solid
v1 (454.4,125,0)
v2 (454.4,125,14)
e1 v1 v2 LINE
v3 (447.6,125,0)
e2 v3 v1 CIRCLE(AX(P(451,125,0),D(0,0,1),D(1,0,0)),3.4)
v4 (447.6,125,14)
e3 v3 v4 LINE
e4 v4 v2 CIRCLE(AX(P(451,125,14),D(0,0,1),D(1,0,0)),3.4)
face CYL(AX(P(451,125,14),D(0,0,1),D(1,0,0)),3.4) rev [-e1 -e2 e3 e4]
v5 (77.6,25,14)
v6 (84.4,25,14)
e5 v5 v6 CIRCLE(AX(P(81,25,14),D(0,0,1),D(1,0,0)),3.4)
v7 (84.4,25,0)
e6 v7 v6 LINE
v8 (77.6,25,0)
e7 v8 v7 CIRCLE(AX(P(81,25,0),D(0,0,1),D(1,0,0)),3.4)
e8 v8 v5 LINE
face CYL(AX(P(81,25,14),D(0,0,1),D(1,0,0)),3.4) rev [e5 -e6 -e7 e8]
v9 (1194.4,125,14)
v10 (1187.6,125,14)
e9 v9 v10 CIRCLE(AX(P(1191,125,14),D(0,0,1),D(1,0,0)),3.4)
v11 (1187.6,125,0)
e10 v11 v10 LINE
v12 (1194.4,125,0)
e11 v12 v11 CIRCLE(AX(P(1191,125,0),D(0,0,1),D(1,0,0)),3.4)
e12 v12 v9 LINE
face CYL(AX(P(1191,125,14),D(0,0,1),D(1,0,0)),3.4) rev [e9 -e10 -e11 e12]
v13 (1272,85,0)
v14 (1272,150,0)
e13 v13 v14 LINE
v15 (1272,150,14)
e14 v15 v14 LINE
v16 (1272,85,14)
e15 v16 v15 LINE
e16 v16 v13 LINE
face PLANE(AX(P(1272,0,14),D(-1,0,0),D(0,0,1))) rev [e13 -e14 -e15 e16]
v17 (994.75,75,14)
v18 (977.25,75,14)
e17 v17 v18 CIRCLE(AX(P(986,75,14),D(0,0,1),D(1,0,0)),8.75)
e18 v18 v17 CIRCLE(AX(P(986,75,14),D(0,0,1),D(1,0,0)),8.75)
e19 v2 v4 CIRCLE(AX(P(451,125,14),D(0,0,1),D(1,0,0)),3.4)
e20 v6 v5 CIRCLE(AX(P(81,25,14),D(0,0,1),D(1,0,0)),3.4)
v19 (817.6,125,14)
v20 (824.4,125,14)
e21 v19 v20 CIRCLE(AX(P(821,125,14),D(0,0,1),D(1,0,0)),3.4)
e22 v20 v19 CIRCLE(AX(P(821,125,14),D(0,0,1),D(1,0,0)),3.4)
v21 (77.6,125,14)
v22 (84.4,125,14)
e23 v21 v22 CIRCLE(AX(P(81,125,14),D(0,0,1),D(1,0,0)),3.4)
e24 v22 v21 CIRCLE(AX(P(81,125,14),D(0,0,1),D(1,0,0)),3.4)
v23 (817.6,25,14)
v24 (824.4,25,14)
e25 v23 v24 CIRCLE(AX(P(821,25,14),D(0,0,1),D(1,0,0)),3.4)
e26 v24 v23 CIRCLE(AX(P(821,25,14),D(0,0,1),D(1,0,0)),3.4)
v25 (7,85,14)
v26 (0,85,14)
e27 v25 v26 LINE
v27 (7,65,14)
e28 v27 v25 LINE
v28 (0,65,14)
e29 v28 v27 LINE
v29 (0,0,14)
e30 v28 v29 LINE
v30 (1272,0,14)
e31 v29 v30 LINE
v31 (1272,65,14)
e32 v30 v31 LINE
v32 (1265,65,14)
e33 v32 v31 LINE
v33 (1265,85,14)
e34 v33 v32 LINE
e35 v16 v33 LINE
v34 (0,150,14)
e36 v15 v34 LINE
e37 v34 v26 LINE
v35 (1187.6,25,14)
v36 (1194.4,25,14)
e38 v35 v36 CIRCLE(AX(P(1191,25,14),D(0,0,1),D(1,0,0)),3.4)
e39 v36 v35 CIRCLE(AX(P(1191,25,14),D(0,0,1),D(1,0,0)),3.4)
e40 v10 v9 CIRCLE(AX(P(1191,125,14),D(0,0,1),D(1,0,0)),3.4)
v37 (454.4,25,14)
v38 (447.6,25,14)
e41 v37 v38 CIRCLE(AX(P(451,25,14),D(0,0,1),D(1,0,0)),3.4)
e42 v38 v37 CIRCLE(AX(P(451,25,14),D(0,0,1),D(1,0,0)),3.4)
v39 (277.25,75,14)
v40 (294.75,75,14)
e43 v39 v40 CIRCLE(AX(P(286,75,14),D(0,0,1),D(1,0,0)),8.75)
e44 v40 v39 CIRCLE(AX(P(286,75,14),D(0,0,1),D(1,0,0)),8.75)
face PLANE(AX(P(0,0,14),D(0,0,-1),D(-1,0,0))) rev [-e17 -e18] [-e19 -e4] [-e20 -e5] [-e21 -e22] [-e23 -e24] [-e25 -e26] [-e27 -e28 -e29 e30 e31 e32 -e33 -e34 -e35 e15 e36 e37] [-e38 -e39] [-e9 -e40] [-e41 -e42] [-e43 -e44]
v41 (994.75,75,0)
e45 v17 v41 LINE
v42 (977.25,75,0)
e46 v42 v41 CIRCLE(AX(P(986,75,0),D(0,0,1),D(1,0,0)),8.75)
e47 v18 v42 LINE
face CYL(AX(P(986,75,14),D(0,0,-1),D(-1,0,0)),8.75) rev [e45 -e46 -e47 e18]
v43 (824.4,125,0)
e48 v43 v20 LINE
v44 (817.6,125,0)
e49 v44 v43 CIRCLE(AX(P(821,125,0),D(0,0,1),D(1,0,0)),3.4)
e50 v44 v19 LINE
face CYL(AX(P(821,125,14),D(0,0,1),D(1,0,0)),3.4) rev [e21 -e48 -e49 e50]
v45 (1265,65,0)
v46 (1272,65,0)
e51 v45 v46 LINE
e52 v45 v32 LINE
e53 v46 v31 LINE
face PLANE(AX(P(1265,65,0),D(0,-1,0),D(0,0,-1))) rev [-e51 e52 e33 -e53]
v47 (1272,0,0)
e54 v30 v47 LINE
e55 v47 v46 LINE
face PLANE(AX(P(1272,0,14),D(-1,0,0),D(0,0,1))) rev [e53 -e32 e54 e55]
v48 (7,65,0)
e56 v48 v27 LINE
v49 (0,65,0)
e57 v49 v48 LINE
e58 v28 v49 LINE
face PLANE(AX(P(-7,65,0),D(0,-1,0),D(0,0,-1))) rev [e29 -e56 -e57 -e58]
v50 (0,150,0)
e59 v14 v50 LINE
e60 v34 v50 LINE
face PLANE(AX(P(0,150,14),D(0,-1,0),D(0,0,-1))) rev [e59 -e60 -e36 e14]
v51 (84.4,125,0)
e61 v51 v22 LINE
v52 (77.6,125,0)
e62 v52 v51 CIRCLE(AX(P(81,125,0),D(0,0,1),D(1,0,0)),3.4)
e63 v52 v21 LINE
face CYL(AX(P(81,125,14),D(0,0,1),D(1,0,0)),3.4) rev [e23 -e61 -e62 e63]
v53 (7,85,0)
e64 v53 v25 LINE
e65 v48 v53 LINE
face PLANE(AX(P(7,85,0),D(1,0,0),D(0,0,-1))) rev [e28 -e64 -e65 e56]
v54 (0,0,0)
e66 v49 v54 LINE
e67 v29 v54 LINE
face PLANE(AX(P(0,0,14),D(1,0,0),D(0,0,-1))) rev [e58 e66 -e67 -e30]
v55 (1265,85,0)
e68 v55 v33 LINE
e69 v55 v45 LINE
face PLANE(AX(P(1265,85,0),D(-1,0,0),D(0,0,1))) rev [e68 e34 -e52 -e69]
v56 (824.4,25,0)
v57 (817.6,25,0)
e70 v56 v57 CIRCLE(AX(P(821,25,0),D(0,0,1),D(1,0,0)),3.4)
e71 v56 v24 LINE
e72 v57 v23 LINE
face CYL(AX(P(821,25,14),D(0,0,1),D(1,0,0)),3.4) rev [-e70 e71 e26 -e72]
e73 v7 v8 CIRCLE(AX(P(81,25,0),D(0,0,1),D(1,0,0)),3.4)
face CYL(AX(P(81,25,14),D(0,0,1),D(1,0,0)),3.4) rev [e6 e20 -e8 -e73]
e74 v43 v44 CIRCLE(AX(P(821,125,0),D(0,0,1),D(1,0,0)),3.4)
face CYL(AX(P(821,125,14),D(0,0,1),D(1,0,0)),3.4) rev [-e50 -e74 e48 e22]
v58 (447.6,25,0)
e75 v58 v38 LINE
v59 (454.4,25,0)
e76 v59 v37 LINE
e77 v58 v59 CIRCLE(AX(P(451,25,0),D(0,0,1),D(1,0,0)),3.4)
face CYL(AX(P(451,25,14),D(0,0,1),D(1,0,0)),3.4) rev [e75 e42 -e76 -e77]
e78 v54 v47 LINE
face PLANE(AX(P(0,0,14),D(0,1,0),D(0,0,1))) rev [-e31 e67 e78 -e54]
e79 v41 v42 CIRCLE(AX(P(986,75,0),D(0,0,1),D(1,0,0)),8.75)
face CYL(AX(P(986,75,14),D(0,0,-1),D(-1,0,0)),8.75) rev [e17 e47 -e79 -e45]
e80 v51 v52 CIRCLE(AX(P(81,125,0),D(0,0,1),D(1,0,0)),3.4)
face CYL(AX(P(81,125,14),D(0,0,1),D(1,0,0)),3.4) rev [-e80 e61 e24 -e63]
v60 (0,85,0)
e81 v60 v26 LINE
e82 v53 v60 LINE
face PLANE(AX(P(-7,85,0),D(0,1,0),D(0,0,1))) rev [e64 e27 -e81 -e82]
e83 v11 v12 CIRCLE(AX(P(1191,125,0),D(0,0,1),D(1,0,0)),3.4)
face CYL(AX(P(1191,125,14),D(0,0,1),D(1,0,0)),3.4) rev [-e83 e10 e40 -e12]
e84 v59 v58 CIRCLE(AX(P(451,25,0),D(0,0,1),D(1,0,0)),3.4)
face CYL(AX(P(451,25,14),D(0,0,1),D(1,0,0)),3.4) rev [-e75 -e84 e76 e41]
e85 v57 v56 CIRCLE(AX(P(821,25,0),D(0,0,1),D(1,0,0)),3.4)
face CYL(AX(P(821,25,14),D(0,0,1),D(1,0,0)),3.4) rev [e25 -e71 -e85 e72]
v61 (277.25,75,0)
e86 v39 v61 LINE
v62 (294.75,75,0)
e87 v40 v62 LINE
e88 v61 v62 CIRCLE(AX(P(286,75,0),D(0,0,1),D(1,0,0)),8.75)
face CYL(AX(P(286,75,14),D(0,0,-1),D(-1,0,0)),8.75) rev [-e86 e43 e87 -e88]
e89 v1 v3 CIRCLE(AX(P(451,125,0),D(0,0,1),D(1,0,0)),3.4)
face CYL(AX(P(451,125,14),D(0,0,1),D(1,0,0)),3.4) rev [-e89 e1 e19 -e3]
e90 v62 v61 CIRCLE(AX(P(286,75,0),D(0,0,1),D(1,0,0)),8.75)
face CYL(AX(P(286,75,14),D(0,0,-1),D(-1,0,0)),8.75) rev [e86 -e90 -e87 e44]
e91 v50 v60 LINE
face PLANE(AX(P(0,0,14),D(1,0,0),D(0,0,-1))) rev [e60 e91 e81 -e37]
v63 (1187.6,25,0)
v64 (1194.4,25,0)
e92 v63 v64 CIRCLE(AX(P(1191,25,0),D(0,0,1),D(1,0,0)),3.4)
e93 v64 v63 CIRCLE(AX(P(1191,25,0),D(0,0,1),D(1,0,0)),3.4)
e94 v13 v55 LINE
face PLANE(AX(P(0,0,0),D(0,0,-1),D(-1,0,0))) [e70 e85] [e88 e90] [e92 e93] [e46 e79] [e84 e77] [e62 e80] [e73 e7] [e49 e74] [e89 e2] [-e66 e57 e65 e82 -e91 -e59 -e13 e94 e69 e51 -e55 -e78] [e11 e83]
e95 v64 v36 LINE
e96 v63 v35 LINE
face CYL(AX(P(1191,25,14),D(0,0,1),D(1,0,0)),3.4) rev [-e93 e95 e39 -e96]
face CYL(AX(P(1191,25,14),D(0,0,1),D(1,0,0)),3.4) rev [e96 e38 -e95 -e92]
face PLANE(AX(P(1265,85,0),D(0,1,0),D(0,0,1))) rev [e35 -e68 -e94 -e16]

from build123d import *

# Parameters (mm, degrees)
SKETCH1_W           = 1272
SKETCH1_H           = 150
SKETCH1_R           = 8.75
BOSS_EXTRUDE1_DEPTH = 14
M8_TAPPED_HOLE1_D   = 6.8
SKETCH5_W           = 14
SKETCH5_H           = 20
CUT_EXTRUDE1_DEPTH  = 1281.890315367


with BuildPart() as part:
    # Sketch1 → Boss-Extrude1 (new body)
    with BuildSketch(Plane.XY):
        with Locations((636, 75)):
            Rectangle(SKETCH1_W, SKETCH1_H)
        with Locations((286, 75)):
            Circle(SKETCH1_R, mode=Mode.SUBTRACT)
        with Locations((986, 75)):
            Circle(SKETCH1_R, mode=Mode.SUBTRACT)
    extrude(amount=BOSS_EXTRUDE1_DEPTH)

    # M8 Tapped Hole1 (through all)
    with Locations(Plane(origin=(81, 125, 14), x_dir=(1, 0, 0), z_dir=(0, 0, 1))):
        with Locations((0, 0), (0, -100), (370, 0), (370, -100), (740, 0), (740, -100), (1110, 0), (1110, -100)):
            Hole(M8_TAPPED_HOLE1_D / 2)

    # Sketch5 → Cut-Extrude1 (cut, through all)
    with BuildSketch(Plane.XY.offset(14)):
        with Locations((0, 75)):
            Rectangle(SKETCH5_W, SKETCH5_H)
        with Locations((1272, 75)):
            Rectangle(SKETCH5_W, SKETCH5_H)
    extrude(amount=-CUT_EXTRUDE1_DEPTH, mode=Mode.SUBTRACT)


solid = part.part
